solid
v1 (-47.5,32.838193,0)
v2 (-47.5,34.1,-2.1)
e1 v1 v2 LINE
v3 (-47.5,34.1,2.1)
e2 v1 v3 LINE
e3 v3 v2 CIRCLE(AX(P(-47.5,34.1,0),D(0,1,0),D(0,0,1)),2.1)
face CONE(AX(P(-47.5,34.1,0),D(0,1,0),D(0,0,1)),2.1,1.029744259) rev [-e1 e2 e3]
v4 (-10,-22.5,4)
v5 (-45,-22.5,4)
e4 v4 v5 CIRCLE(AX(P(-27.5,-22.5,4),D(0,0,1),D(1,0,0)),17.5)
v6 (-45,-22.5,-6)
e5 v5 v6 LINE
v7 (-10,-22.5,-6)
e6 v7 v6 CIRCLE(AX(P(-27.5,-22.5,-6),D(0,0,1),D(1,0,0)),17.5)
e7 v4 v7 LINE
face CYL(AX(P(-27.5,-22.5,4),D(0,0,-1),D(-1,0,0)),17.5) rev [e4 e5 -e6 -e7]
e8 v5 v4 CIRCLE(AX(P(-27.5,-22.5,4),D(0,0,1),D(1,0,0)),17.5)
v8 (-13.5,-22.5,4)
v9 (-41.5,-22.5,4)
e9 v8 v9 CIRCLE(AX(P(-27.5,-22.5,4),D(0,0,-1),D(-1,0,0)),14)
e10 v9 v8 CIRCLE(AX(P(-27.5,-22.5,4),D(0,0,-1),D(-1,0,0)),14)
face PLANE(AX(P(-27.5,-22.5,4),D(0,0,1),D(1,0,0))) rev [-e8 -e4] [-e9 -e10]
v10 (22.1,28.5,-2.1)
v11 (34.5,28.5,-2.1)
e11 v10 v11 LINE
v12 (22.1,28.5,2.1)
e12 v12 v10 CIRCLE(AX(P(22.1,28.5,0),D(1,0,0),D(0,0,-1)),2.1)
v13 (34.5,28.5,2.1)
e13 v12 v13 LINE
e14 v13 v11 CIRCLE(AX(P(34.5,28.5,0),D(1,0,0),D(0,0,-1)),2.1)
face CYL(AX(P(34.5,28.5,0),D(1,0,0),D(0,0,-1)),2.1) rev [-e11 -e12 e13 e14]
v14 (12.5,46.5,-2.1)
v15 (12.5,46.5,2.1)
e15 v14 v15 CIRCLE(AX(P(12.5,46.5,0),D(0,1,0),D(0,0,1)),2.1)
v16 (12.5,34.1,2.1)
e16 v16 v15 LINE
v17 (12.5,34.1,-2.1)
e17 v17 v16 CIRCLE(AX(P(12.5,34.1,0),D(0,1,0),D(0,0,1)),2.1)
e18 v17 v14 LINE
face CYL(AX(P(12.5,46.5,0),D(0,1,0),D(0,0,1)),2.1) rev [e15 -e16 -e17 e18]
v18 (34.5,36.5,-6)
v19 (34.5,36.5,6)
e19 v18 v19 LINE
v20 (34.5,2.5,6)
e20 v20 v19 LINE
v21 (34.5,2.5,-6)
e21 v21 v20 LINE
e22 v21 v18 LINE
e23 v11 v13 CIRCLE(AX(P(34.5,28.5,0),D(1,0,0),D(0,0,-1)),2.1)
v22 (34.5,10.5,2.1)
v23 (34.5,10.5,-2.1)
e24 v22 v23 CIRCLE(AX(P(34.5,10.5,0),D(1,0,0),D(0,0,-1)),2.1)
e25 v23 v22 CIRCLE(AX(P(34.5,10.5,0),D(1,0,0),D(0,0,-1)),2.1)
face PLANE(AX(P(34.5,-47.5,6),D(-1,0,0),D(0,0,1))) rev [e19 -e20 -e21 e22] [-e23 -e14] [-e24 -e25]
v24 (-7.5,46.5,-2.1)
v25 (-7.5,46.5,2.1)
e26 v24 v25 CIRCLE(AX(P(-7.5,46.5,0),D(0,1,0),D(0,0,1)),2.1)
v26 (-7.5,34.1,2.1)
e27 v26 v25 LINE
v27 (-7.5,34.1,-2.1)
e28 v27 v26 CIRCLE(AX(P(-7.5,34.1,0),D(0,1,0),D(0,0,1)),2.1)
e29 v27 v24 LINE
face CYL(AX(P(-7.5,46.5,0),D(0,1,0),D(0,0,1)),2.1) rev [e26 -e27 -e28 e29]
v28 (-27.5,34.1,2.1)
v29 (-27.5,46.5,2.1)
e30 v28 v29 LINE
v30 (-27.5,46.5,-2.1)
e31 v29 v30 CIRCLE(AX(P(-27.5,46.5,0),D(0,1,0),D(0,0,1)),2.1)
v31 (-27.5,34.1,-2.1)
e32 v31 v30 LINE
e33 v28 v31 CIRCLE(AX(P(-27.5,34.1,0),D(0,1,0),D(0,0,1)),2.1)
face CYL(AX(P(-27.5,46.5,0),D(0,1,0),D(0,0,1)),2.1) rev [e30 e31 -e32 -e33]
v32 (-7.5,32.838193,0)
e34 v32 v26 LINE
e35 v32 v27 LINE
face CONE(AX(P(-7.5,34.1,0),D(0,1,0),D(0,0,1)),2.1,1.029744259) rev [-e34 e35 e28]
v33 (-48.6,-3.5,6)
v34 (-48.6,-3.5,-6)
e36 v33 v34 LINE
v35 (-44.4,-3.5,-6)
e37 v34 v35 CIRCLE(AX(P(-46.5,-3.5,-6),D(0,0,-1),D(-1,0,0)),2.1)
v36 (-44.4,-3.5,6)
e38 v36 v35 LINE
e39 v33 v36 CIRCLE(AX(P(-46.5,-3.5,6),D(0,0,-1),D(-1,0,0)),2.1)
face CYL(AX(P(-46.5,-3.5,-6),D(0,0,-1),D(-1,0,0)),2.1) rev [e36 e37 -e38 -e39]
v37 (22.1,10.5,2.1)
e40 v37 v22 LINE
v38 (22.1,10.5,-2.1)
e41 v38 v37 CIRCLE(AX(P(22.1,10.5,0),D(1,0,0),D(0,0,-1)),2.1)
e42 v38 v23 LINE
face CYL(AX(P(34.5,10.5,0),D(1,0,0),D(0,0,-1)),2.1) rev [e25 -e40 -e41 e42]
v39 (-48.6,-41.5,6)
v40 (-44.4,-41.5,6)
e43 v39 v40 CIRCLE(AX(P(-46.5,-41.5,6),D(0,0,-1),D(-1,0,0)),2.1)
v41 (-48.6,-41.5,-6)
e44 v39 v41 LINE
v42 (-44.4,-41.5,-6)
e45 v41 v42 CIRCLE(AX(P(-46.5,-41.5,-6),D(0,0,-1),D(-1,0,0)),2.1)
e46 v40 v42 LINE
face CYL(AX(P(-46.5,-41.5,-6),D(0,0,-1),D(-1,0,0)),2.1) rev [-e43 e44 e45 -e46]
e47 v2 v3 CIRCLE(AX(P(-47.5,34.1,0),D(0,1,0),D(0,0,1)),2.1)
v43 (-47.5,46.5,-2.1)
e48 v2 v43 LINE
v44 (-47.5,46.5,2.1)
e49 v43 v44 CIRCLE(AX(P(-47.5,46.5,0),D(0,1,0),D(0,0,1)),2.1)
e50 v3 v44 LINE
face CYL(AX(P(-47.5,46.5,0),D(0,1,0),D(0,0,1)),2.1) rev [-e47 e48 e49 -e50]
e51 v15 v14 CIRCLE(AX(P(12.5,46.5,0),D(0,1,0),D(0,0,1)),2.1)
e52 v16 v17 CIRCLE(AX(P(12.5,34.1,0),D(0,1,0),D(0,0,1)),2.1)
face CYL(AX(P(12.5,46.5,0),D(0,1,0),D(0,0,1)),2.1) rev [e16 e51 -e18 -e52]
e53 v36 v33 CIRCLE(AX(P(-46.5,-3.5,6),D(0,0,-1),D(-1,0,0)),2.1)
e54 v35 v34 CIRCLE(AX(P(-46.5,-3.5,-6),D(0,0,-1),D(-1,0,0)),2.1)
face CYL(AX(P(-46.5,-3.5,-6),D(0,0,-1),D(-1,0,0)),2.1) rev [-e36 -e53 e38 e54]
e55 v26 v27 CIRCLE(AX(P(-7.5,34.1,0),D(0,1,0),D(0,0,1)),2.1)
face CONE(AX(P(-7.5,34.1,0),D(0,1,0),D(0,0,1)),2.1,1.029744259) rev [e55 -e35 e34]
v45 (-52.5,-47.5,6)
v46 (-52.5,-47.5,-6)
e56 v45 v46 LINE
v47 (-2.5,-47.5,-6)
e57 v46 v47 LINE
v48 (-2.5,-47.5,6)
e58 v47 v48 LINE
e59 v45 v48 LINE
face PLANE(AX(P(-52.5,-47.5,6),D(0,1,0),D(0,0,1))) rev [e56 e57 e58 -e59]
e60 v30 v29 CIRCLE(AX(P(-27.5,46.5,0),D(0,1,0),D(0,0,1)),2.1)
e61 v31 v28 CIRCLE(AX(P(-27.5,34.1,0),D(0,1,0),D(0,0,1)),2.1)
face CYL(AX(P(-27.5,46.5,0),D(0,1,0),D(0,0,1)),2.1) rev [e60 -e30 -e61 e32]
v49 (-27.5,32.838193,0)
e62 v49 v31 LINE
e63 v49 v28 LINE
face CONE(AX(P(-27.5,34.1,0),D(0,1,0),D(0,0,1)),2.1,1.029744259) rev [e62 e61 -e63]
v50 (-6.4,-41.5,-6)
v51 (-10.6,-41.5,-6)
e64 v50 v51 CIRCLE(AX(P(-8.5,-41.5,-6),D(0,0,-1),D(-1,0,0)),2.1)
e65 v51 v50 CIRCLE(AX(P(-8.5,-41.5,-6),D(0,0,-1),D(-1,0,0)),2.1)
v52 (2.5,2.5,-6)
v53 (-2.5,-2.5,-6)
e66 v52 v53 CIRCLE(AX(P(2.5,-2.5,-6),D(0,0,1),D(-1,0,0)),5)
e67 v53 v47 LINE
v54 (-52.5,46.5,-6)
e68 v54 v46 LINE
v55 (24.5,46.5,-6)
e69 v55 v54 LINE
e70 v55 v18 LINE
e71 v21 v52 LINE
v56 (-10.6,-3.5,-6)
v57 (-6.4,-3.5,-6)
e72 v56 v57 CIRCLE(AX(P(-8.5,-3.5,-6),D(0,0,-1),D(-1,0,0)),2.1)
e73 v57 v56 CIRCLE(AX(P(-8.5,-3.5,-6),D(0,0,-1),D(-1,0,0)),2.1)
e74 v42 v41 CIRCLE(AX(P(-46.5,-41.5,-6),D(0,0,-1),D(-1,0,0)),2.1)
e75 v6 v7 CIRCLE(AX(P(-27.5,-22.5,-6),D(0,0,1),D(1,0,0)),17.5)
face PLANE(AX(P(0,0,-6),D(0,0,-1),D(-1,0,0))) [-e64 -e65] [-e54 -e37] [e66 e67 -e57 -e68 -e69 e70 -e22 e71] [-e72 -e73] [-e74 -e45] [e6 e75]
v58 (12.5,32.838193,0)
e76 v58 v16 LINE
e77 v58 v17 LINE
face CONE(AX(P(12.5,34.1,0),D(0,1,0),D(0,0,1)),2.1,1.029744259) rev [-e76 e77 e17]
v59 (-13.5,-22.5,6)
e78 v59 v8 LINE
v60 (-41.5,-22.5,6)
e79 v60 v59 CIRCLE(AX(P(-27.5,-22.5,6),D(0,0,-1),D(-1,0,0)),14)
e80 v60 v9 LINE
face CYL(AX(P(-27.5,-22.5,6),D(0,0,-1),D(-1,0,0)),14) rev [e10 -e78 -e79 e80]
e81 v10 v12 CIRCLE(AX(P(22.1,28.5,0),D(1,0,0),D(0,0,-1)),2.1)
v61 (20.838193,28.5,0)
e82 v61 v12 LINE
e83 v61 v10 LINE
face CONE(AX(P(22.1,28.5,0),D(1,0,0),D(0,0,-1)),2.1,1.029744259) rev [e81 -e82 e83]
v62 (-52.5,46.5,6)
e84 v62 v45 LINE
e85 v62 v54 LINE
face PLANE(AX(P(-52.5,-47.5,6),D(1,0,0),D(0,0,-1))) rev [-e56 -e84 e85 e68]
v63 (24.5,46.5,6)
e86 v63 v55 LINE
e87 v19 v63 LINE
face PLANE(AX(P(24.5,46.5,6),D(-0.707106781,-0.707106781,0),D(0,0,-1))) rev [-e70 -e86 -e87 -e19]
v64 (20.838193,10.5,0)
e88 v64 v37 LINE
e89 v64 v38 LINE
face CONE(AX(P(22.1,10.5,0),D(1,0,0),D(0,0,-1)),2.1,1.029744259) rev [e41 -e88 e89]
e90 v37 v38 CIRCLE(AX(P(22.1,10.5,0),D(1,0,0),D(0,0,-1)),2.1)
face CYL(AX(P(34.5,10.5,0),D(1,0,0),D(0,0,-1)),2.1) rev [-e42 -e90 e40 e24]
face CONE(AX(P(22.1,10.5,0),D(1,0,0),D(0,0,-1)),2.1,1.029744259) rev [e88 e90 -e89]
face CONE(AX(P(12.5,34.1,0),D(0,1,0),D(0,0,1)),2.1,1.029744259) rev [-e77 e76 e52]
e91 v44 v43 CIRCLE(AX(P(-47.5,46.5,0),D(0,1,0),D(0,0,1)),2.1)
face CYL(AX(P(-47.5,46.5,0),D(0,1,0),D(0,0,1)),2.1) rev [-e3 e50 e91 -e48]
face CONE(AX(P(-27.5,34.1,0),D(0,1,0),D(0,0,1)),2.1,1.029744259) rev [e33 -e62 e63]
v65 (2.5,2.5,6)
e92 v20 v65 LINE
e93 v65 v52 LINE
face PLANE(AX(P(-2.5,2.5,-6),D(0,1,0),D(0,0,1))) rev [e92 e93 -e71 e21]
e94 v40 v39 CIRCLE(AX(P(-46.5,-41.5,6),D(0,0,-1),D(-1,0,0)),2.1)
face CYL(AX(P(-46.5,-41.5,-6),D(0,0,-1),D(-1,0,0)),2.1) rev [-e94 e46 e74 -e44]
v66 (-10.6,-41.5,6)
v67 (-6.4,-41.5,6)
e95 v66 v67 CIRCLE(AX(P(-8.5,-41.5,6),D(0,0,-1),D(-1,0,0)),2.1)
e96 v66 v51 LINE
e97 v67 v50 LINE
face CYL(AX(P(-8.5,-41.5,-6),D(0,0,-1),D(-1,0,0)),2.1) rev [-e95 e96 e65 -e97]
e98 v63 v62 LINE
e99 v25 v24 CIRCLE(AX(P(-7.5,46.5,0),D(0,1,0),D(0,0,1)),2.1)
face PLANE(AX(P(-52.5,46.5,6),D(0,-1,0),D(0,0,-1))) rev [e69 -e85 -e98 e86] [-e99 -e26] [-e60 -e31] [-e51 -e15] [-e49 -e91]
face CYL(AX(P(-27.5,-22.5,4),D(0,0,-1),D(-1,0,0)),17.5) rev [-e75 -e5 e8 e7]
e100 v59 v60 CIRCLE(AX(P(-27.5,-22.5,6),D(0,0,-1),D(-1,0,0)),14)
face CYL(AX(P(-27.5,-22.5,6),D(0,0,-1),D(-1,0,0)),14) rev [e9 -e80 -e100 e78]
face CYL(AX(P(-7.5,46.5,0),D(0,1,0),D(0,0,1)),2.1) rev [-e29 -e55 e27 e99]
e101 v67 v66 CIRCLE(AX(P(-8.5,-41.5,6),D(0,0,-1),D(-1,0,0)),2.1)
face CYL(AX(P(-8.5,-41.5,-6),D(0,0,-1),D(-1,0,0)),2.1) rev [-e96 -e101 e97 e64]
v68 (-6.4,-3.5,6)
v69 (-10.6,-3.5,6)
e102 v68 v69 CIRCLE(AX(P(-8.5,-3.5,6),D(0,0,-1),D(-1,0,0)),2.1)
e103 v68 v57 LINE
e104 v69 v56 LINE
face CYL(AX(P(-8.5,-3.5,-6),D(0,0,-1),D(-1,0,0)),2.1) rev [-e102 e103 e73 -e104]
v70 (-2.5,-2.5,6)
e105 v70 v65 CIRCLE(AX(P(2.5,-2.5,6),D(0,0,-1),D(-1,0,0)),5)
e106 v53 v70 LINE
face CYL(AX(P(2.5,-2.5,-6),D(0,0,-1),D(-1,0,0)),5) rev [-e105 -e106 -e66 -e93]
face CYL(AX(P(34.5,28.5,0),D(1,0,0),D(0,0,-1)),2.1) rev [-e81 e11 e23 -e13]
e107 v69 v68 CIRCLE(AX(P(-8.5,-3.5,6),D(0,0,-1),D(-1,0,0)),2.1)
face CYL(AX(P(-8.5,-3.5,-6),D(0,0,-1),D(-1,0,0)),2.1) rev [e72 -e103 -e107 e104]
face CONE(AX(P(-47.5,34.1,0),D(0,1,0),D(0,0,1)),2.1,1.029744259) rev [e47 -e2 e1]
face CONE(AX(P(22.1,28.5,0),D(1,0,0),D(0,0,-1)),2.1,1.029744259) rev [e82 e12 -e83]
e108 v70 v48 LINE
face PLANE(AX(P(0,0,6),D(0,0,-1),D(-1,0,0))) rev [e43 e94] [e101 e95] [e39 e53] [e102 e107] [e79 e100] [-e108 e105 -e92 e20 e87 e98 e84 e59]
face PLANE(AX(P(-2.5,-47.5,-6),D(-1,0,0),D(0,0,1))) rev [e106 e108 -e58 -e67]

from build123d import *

# Parameters (mm, degrees)
SKETCH_1_W             = 105
SKETCH_1_H             = 95
EXTRUDE_1_DEPTH        = 6
SKETCH_10_R            = 17.5
CUT_EXTRUDE_1_DEPTH    = 10
SKETCH_12_R            = 14
CUT_EXTRUDE_2_DEPTH    = 72.50174823
SKETCH_13_W            = 55
SKETCH_13_H            = 50
CUT_EXTRUDE_3_DEPTH    = 72.808773837
FILLET_1_R             = 5
HOLE_WIZARD_M5_2_D     = 4.2
MOVE_FACE_1_BY         = 1
MOVE_FACE_2_BY         = 18
CHAMFER_2_SIZE         = 10
HOLE_WIZARD_M5_3_D     = 4.2
HOLE_WIZARD_M5_3_DEPTH = 12.4
HOLE_WIZARD_M5_3_TIP   = 1.2618073
HOLE_WIZARD_M5_4_D     = 4.2
HOLE_WIZARD_M5_4_DEPTH = 12.4
HOLE_WIZARD_M5_4_TIP   = 1.2618073


with BuildPart() as part:
    # 草图1 → 凸台-拉伸1 (new, symmetric)
    with BuildSketch(Plane.XY):
        Rectangle(SKETCH_1_W, SKETCH_1_H)
    extrude(amount=EXTRUDE_1_DEPTH, both=True)

    # 草图10 → 切除-拉伸1 (cut)
    with BuildSketch(Plane.XY.offset(-6)):
        with Locations((-27.5, -22.5)):
            Circle(SKETCH_10_R)
    extrude(amount=CUT_EXTRUDE_1_DEPTH, mode=Mode.SUBTRACT)

    # 草图12 → 切除-拉伸2 (cut, through all)
    with BuildSketch(Plane(origin=(0, 0, 4), x_dir=(-1, 0, 0), z_dir=(0, 0, -1))):
        with Locations((27.5, -22.5)):
            Circle(SKETCH_12_R)
    extrude(amount=-CUT_EXTRUDE_2_DEPTH, mode=Mode.SUBTRACT)

    # 草图13 → 切除-拉伸3 (cut, through all)
    with BuildSketch(Plane.XY.offset(6)):
        with Locations((25, -22.5)):
            Rectangle(SKETCH_13_W, SKETCH_13_H)
    extrude(amount=-CUT_EXTRUDE_3_DEPTH, mode=Mode.SUBTRACT)

    # 圆角1
    fillet_1_edges = [part.edges().sort_by_distance(p)[0] for p in [
        (-2.5, 2.5, 0),
    ]]
    fillet(fillet_1_edges, radius=FILLET_1_R)

    # M5 螺纹孔2 (through all)
    with Locations(Plane(origin=(0, 0, -6), x_dir=(-1, 0, 0), z_dir=(0, 0, -1))):
        with Locations((8.5, -3.5), (8.5, -41.5), (46.5, -41.5), (46.5, -3.5)):
            Hole(HOLE_WIZARD_M5_2_D / 2)

    # Move Face 1: a face moved inward by 1.0
    extrude(part.faces().sort_by_distance((0, 47.5, 0))[0], amount=MOVE_FACE_1_BY, dir=(0, -1, 0), mode=Mode.SUBTRACT)

    # Move Face 2: a face moved inward by 18.0
    extrude(part.faces().sort_by_distance((52.5, 24.5, 0))[0], amount=MOVE_FACE_2_BY, dir=(-1, 0, 0), mode=Mode.SUBTRACT)

    # 倒角2
    chamfer_2_edges = [part.edges().sort_by_distance(p)[0] for p in [
        (34.5, 46.5, 0),
    ]]
    chamfer(chamfer_2_edges, length=CHAMFER_2_SIZE)

    # M5 螺纹孔3
    with Locations(Plane(origin=(0, 46.5, 0), x_dir=(1, 0, 0), z_dir=(0, 1, 0))):
        with Locations((12.5, 0), (-7.5, 0), (-27.5, 0), (-47.5, 0)):
            Hole(HOLE_WIZARD_M5_3_D / 2, depth=HOLE_WIZARD_M5_3_DEPTH)
            with Locations((0, 0, -(HOLE_WIZARD_M5_3_DEPTH + HOLE_WIZARD_M5_3_TIP / 2))):  # 118° drill point
                Cone(0, HOLE_WIZARD_M5_3_D / 2, HOLE_WIZARD_M5_3_TIP, mode=Mode.SUBTRACT)

    # M5 螺纹孔4
    with Locations(Plane(origin=(34.5, 0, 0), x_dir=(0, 0, -1), z_dir=(1, 0, 0))):
        with Locations((0, 28.5), (0, 10.5)):
            Hole(HOLE_WIZARD_M5_4_D / 2, depth=HOLE_WIZARD_M5_4_DEPTH)
            with Locations((0, 0, -(HOLE_WIZARD_M5_4_DEPTH + HOLE_WIZARD_M5_4_TIP / 2))):  # 118° drill point
                Cone(0, HOLE_WIZARD_M5_4_D / 2, HOLE_WIZARD_M5_4_TIP, mode=Mode.SUBTRACT)


solid = part.part
